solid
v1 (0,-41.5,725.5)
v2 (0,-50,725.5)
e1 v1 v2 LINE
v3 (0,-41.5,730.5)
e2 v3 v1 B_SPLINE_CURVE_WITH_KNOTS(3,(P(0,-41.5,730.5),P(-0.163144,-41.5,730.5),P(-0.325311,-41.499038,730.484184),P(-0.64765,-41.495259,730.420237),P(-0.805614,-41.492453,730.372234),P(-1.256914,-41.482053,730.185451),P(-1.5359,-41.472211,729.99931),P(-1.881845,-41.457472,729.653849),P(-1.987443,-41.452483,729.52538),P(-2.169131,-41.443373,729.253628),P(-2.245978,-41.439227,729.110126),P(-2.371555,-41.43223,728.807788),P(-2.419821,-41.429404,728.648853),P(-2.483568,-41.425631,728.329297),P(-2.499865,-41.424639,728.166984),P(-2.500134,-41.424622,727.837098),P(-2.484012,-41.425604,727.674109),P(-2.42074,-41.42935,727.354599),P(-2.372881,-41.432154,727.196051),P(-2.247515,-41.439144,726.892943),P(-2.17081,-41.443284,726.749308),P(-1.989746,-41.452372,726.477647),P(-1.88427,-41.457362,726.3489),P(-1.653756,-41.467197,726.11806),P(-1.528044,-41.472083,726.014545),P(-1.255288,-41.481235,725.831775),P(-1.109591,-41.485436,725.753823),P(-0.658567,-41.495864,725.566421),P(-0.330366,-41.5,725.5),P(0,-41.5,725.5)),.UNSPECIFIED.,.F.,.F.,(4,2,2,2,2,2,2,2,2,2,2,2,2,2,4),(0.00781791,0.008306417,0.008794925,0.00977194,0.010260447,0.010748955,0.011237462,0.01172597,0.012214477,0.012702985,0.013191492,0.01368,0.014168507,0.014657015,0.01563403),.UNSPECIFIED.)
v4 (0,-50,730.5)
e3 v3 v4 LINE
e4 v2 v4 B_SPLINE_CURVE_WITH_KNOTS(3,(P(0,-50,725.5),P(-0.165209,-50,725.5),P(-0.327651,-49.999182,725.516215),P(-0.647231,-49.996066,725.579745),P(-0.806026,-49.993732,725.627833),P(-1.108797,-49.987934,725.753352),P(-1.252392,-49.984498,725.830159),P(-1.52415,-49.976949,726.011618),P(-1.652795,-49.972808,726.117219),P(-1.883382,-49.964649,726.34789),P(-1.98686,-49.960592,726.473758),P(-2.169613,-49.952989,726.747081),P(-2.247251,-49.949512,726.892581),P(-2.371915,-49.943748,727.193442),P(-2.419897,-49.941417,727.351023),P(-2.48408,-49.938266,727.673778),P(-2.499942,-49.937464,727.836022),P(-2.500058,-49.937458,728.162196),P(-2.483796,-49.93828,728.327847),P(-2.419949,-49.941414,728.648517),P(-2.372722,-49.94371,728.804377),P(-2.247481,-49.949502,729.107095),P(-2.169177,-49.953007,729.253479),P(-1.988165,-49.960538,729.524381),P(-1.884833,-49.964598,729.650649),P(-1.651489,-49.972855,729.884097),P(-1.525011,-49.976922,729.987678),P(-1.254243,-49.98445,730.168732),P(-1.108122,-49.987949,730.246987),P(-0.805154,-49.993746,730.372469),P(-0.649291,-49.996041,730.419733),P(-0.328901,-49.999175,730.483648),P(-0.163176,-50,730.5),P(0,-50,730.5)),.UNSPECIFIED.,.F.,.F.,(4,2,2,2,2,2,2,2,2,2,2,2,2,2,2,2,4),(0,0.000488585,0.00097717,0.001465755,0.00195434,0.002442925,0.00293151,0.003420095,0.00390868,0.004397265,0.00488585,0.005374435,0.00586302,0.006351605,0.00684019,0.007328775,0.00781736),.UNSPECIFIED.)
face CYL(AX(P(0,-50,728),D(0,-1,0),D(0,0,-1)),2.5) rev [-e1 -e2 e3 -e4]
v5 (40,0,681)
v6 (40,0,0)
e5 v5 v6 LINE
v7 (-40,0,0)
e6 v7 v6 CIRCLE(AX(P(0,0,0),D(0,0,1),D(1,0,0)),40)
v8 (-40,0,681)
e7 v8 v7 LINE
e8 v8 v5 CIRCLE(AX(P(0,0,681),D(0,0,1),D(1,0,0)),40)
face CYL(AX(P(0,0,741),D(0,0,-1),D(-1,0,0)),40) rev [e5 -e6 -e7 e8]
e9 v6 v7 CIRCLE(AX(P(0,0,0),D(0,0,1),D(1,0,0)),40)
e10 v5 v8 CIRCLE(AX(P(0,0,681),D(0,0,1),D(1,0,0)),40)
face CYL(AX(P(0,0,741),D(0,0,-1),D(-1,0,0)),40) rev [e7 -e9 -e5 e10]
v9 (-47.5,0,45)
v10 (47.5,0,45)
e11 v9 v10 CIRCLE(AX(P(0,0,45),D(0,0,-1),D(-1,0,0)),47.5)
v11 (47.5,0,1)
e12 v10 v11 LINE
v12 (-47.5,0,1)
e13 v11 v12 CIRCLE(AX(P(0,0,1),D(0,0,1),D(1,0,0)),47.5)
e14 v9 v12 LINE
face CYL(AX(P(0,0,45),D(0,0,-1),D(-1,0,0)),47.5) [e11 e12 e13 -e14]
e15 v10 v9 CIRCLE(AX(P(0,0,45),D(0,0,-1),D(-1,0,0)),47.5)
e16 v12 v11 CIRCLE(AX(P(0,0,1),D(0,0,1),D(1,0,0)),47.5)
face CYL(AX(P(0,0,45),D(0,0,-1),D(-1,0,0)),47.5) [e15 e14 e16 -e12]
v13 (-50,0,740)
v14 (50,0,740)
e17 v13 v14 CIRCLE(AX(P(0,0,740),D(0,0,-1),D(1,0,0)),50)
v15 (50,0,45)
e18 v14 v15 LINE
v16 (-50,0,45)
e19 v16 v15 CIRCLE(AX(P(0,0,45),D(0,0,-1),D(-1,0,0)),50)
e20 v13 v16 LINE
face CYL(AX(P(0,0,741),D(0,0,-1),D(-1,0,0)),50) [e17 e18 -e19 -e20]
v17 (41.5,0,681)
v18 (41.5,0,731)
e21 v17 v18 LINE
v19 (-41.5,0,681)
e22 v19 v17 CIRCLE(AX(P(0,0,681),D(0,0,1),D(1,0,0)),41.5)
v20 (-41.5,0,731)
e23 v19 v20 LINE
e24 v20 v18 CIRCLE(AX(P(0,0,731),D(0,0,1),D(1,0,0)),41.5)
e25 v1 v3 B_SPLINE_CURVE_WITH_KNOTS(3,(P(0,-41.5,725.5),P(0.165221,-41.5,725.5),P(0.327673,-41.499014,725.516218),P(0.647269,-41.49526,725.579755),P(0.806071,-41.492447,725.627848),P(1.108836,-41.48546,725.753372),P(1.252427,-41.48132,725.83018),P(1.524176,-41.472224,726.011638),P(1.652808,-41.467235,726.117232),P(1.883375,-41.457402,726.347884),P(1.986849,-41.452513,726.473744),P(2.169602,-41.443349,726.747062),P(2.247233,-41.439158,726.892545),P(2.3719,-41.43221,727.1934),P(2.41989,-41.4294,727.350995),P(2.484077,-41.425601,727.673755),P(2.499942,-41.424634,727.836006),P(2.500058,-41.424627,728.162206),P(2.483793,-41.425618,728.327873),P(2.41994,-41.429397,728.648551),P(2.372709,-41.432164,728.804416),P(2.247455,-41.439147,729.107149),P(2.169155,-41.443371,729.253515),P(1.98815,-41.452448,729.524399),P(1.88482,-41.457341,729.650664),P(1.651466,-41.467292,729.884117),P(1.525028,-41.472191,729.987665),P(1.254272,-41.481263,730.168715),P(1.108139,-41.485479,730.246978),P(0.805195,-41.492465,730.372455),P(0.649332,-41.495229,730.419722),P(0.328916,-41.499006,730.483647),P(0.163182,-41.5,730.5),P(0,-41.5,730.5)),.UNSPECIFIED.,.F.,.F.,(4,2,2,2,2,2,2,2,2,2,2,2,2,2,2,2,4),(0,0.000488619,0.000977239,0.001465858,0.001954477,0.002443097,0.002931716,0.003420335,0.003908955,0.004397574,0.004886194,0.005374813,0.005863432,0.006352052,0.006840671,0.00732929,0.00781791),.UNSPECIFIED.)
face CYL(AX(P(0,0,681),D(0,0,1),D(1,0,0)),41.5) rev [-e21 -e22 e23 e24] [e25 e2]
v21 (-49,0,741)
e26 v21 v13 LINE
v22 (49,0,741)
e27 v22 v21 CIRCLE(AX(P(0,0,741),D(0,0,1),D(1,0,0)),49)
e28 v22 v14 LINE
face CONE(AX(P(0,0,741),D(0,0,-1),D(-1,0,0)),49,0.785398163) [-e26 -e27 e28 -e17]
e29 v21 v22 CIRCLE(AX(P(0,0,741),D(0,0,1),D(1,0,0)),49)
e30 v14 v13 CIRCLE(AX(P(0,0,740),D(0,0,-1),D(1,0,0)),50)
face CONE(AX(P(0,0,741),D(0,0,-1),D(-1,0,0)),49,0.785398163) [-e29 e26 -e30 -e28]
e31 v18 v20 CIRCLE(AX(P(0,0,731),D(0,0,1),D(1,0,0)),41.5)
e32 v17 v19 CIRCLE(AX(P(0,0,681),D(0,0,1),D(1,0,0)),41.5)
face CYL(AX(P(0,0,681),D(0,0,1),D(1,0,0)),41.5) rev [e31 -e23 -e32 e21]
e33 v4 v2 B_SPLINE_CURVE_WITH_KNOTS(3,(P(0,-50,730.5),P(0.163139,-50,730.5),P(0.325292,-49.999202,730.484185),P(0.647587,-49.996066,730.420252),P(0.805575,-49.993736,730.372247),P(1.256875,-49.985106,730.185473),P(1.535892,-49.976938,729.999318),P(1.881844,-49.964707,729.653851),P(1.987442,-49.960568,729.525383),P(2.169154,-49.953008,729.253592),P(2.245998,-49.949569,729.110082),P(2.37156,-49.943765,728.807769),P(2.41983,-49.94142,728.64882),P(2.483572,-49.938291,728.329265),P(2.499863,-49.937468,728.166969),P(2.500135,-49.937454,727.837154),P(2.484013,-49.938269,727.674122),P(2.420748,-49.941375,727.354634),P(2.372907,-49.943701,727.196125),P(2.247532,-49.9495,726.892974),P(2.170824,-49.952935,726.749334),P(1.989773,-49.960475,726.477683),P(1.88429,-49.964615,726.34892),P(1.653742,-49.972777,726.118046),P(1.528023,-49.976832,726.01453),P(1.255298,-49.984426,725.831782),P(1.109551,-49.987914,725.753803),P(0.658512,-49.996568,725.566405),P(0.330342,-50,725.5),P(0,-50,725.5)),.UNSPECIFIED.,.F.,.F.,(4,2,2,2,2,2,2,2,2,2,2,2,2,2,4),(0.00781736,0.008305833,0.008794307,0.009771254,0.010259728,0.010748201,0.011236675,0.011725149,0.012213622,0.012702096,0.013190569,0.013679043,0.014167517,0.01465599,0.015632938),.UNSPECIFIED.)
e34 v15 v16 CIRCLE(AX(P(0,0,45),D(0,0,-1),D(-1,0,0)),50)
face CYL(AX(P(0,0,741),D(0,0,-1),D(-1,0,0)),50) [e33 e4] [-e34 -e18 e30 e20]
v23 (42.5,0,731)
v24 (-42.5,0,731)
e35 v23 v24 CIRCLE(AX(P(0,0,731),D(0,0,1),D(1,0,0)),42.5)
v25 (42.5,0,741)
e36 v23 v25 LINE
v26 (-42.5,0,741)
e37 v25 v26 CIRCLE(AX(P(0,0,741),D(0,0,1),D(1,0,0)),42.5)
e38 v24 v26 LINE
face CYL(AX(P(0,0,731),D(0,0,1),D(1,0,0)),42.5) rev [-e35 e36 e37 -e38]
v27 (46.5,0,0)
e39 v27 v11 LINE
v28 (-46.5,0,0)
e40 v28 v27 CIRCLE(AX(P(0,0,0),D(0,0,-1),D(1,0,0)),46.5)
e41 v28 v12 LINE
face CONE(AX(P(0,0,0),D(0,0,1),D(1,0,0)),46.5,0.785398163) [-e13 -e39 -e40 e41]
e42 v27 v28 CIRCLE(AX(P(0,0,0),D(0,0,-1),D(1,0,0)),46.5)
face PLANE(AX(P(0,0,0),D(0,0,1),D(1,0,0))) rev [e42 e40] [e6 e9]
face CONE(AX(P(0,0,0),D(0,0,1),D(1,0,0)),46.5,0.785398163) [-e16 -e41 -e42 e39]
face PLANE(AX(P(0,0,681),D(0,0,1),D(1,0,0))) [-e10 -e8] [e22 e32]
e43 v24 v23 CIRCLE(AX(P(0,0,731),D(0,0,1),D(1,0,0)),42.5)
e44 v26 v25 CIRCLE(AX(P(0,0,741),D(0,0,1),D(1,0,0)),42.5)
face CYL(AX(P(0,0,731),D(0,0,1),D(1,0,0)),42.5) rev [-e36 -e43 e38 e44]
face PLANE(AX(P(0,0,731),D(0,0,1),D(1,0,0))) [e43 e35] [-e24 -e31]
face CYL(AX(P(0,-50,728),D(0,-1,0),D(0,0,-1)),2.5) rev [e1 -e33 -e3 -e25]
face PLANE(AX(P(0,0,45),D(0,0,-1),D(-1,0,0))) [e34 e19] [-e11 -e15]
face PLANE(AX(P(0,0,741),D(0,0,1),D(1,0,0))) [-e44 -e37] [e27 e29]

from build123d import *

# Parameters (mm, degrees)
SKETCH1_R             = 50
SKETCH1_R_2           = 40
BOSS_EXTRUDE1_DEPTH   = 741
SKETCH2_R             = 61.681035311
SKETCH2_R_2           = 47.5
CUT_EXTRUDE1_DEPTH    = 45
CHAMFER1_SIZE         = 1
CHAMFER2_SIZE         = 1
SKETCH10_R            = 42.5
CUT_EXTRUDE9_DEPTH    = 10
SKETCH11_R            = 41.5
CUT_EXTRUDE10_DEPTH   = 50
M6_TAPPED_HOLE1_D     = 5
M6_TAPPED_HOLE1_DEPTH = 15
M6_TAPPED_HOLE1_TIP   = 1.502151548


with BuildPart() as part:
    # Sketch1 → Boss-Extrude1 (new body)
    with BuildSketch(Plane.XY):
        Circle(SKETCH1_R)
        Circle(SKETCH1_R_2, mode=Mode.SUBTRACT)
    extrude(amount=BOSS_EXTRUDE1_DEPTH)

    # Sketch2 → Cut-Extrude1 (cut)
    with BuildSketch(Plane(origin=(0, 0, 0), x_dir=(-1, 0, 0), z_dir=(0, 0, -1))):
        Circle(SKETCH2_R)
        Circle(SKETCH2_R_2, mode=Mode.SUBTRACT)
    extrude(amount=-CUT_EXTRUDE1_DEPTH, mode=Mode.SUBTRACT)

    # Chamfer1
    chamfer1_edges = [part.edges().sort_by_distance(p)[0] for p in [
        (47.5, 0, 0),
    ]]
    chamfer(chamfer1_edges, length=CHAMFER1_SIZE)

    # Chamfer2
    chamfer2_edges = [part.edges().sort_by_distance(p)[0] for p in [
        (-50, 0, 741),
    ]]
    chamfer(chamfer2_edges, length=CHAMFER2_SIZE)

    # Sketch10 → Cut-Extrude9 (cut)
    with BuildSketch(Plane.XY.offset(741)):
        Circle(SKETCH10_R)
    extrude(amount=-CUT_EXTRUDE9_DEPTH, mode=Mode.SUBTRACT)

    # Sketch11 → Cut-Extrude10 (cut)
    with BuildSketch(Plane.XY.offset(731)):
        Circle(SKETCH11_R)
    extrude(amount=-CUT_EXTRUDE10_DEPTH, mode=Mode.SUBTRACT)

    # M6 Tapped Hole1
    with Locations(Plane.XZ.offset(50)):
        with Locations((0, 728)):
            Hole(M6_TAPPED_HOLE1_D / 2, depth=M6_TAPPED_HOLE1_DEPTH)
            with Locations((0, 0, -(M6_TAPPED_HOLE1_DEPTH + M6_TAPPED_HOLE1_TIP / 2))):  # 118° drill point
                Cone(0, M6_TAPPED_HOLE1_D / 2, M6_TAPPED_HOLE1_TIP, mode=Mode.SUBTRACT)


solid = part.part
